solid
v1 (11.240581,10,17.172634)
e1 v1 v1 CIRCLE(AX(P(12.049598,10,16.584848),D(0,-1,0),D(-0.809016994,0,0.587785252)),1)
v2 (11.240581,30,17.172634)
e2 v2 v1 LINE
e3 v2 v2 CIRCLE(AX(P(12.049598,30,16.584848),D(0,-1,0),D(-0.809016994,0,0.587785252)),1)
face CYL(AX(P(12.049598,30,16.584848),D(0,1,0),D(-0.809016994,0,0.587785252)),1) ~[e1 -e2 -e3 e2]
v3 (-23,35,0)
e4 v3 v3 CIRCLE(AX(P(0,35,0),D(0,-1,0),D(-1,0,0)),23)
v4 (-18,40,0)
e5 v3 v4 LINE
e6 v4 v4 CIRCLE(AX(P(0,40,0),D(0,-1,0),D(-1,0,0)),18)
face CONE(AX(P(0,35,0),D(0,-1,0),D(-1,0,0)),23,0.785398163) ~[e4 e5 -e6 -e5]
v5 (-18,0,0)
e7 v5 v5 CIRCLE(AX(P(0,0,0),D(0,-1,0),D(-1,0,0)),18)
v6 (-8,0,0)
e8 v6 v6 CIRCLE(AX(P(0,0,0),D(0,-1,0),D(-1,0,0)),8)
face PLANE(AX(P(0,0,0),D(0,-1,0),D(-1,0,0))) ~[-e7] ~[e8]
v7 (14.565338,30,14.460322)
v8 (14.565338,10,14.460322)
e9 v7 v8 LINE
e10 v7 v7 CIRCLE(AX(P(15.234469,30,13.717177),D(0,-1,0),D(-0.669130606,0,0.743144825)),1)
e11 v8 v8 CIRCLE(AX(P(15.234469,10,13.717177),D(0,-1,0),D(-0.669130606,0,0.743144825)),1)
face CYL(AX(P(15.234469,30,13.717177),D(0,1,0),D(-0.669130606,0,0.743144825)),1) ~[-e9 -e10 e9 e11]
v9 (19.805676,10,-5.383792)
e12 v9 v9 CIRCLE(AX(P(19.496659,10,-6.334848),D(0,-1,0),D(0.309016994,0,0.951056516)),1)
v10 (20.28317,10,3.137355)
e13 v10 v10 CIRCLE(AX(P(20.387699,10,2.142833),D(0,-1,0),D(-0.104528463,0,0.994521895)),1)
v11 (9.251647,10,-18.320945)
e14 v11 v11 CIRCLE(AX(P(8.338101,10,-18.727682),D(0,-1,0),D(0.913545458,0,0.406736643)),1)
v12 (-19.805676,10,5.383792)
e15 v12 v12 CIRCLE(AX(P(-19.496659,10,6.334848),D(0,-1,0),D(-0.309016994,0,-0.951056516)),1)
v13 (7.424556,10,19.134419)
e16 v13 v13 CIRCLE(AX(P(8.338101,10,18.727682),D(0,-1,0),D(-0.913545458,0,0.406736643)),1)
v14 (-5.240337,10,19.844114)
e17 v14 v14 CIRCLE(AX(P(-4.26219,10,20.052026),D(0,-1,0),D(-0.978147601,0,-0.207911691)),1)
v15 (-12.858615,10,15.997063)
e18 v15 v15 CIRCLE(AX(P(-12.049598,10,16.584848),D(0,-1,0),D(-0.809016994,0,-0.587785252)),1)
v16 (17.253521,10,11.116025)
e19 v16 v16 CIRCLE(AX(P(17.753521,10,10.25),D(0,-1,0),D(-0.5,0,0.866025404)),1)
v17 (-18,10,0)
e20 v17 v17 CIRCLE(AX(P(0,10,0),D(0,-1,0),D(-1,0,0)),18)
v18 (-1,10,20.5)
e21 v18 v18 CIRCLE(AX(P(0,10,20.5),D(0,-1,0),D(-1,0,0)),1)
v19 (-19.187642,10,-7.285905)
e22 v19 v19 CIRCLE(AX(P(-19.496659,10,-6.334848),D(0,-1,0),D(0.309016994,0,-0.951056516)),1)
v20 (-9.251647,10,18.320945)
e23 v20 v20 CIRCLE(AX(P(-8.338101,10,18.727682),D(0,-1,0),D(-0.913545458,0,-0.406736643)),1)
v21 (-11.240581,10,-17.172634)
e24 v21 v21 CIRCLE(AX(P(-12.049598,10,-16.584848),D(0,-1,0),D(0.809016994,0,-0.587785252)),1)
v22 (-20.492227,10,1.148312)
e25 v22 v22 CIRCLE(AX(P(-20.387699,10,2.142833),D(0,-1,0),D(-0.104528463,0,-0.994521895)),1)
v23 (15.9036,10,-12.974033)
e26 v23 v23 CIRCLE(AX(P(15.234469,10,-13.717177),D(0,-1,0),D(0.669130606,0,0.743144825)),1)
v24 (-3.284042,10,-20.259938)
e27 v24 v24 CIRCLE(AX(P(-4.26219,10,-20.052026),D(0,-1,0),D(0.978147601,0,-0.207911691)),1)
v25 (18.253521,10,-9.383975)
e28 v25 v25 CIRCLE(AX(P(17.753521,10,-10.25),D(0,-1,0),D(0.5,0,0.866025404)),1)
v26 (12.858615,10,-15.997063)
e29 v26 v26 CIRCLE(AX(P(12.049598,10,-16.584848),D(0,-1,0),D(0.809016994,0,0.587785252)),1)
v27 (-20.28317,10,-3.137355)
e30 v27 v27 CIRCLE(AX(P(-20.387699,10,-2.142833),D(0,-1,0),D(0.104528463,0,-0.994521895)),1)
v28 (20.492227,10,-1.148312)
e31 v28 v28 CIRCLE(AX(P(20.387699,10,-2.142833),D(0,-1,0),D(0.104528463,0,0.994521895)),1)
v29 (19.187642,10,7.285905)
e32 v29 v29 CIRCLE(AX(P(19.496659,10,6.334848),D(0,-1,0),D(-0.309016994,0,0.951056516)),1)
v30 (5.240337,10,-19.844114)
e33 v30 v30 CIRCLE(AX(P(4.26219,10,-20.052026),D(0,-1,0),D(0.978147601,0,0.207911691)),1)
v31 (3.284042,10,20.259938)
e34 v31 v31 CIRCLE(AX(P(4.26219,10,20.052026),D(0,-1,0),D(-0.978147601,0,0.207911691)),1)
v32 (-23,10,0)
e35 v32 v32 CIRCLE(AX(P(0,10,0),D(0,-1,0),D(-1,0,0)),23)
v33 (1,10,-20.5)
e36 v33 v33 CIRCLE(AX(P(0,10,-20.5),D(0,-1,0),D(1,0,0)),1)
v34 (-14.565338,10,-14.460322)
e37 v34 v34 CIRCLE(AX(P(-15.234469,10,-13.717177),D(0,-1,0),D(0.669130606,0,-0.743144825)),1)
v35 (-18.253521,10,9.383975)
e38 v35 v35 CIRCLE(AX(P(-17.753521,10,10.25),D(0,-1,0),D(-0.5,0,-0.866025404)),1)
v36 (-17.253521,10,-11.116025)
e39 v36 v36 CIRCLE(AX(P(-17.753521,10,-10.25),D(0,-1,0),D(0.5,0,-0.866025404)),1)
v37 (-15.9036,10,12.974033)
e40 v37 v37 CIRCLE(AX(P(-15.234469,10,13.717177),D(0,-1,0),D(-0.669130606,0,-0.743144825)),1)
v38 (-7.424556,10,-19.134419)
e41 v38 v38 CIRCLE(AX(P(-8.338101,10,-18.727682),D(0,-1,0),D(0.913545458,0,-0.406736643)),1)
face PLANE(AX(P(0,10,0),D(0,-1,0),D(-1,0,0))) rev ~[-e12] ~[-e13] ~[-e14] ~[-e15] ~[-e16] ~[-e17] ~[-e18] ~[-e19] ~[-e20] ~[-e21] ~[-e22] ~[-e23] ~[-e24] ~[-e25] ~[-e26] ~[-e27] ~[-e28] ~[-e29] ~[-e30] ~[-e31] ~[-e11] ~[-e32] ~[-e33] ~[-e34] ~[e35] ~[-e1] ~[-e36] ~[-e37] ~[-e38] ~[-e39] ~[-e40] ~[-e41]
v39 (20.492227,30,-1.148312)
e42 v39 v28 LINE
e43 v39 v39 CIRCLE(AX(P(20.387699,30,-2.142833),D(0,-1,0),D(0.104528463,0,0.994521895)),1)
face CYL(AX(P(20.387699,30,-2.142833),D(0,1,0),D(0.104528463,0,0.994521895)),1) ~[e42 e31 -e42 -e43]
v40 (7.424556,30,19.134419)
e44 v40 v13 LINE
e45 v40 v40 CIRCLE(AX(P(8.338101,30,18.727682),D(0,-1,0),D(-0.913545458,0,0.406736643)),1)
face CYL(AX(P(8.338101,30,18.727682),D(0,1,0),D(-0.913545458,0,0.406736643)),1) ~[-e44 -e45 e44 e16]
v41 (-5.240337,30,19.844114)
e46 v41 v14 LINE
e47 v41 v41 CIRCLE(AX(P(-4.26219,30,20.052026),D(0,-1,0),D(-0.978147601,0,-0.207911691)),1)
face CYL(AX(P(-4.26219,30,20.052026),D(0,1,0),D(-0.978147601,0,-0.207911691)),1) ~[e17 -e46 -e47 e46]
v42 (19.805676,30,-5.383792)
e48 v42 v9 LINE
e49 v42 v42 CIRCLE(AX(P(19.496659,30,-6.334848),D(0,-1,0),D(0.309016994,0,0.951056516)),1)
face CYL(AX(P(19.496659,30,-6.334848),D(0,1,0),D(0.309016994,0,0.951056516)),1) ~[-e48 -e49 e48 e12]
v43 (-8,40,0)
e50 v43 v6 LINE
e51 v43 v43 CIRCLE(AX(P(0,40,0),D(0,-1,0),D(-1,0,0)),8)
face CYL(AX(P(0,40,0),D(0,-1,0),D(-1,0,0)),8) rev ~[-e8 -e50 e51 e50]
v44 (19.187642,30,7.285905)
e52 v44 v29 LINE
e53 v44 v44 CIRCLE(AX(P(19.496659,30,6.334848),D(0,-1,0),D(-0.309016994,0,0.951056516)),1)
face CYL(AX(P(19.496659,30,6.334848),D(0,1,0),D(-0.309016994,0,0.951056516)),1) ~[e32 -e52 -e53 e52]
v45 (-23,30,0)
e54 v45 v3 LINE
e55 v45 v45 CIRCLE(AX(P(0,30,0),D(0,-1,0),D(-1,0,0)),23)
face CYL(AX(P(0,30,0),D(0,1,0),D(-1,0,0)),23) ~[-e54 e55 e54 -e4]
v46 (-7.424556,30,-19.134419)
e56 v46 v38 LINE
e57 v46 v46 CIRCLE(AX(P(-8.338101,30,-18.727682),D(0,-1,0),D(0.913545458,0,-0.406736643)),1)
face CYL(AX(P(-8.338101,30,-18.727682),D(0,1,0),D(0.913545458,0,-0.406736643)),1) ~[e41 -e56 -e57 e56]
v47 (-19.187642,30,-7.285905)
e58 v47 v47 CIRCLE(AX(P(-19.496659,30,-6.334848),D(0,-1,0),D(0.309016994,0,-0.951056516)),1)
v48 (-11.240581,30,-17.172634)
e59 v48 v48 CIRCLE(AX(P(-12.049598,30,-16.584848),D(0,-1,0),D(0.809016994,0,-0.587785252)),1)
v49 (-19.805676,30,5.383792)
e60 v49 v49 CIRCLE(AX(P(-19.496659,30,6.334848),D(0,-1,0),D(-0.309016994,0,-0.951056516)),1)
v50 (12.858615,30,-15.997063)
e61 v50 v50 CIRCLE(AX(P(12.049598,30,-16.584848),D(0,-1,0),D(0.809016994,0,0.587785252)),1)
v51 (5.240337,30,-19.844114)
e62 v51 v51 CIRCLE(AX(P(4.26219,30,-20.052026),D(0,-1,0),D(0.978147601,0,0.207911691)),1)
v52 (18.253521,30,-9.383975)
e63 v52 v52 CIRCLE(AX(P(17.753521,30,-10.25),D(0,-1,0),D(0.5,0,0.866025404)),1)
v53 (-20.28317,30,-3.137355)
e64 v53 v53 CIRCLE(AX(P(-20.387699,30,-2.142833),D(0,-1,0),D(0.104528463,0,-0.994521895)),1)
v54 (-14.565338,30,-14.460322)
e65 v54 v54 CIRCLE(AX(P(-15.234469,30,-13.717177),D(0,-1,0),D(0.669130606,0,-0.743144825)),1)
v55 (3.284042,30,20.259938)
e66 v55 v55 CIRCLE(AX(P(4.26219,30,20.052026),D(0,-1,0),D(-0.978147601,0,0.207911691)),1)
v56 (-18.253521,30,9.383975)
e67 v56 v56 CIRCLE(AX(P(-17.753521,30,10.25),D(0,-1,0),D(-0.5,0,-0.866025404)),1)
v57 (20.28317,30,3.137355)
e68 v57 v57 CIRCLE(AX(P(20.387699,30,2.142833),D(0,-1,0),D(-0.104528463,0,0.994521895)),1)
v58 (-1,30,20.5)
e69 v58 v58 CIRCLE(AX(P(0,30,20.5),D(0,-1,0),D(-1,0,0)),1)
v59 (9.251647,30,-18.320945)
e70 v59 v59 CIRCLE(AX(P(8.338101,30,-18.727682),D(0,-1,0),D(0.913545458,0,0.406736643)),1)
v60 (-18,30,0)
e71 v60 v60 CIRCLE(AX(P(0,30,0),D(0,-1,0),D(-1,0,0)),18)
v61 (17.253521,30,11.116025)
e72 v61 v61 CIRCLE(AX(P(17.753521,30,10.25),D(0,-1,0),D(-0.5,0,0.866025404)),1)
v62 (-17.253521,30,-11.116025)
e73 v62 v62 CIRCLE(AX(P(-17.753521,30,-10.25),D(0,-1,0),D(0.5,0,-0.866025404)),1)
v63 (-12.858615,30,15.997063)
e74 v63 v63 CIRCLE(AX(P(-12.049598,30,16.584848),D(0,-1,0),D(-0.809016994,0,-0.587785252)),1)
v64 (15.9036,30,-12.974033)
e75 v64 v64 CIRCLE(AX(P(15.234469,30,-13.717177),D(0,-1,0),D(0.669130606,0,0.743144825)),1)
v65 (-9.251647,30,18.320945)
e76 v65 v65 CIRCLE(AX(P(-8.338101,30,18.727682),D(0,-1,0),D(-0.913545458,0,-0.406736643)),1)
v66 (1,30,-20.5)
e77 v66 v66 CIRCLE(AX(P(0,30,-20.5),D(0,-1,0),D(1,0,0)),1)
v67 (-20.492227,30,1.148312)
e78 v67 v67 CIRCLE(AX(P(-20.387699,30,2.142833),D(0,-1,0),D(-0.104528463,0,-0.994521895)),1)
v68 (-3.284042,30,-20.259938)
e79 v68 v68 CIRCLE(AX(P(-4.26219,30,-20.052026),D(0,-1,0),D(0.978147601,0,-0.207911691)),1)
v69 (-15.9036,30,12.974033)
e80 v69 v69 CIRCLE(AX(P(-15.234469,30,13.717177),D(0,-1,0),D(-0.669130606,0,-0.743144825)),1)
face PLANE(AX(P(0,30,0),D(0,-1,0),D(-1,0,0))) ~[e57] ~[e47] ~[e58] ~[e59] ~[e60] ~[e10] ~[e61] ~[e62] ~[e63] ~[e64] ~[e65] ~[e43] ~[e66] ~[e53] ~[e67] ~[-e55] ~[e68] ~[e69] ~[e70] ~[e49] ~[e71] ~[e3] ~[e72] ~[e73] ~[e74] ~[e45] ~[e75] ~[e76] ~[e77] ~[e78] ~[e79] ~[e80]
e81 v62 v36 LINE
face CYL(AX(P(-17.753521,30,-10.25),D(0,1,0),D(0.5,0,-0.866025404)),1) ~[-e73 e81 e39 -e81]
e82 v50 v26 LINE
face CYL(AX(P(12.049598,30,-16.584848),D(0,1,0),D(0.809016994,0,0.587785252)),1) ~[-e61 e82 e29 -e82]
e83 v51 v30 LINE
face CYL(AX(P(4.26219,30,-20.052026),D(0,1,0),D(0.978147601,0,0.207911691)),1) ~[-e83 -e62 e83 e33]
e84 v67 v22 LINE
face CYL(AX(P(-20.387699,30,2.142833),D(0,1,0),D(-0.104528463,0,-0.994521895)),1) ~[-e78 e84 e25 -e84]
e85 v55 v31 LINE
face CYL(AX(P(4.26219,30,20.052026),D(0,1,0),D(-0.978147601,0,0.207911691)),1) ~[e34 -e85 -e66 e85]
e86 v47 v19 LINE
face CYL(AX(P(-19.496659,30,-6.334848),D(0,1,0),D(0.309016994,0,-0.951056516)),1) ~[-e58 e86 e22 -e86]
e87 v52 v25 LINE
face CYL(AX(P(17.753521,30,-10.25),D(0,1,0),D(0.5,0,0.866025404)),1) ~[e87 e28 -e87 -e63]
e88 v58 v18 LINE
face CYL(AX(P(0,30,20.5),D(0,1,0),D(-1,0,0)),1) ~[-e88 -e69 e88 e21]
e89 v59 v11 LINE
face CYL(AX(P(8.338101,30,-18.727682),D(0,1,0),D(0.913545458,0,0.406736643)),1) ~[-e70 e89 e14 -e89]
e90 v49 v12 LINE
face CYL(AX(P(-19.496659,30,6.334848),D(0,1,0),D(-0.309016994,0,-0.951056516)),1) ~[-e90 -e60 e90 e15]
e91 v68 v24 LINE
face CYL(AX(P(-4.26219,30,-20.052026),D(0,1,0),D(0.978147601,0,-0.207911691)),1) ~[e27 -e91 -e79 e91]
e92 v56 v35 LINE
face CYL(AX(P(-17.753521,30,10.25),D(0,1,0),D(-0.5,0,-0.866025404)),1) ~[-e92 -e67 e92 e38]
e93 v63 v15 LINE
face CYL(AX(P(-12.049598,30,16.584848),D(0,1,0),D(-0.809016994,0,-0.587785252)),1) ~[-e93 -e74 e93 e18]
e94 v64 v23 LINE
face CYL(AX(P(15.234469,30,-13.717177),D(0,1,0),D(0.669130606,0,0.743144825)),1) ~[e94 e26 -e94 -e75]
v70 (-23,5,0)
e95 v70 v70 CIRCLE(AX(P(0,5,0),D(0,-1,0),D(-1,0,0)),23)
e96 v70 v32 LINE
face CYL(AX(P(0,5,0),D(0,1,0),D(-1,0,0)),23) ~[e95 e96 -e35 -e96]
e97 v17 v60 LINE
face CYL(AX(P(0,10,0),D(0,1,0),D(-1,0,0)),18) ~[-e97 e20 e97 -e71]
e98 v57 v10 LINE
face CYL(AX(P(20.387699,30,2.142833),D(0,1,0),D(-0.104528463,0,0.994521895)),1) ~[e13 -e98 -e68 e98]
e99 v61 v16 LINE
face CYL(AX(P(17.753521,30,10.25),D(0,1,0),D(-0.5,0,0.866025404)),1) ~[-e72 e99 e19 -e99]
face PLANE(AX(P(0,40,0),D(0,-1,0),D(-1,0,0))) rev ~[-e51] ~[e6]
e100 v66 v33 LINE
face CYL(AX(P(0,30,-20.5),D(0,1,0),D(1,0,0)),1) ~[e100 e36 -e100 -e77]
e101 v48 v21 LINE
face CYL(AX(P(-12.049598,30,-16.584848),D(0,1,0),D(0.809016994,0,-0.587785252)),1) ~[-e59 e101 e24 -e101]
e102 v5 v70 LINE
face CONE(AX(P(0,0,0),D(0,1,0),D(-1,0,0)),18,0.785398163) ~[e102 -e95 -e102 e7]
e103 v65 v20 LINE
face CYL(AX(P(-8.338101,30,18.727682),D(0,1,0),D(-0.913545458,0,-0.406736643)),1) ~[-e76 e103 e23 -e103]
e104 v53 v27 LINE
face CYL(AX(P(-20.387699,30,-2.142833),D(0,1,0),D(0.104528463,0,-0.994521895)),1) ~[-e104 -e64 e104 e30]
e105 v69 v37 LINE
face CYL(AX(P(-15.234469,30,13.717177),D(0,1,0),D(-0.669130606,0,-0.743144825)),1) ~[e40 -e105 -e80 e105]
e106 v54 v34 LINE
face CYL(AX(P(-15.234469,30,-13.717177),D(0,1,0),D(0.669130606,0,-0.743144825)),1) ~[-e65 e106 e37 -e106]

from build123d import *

# Parameters (mm, degrees)
TOOTH_PROFILE_R         = 1
TOOTH_DEPTH             = 20
TOOTH_PATTERN_30X_COUNT = 30


with BuildPart() as part:
    # Pulley Body Profile → Pulley Body (revolve)
    with BuildSketch(Plane.XY, mode=Mode.PRIVATE) as pulley_body_sk:
        Polygon((8, 40), (8, 0), (18, 0), (23, 5), (23, 10), (18, 10), (18, 30), (23, 30), (23, 35), (18, 40), align=None)
    revolve(pulley_body_sk.sketch.rotate(Axis((0, 32.636363636, 0), (0, -1, 0)), 180), axis=Axis((0, 32.636363636, 0), (0, -1, 0)))

    # Tooth Profile → Tooth (add)
    with BuildSketch(Plane.XZ.offset(-30)):
        with Locations(Location((0, 20.5, 0), (0, 0, 180))):
            Circle(TOOTH_PROFILE_R)
    tooth = extrude(amount=TOOTH_DEPTH)

    # Tooth Pattern 30x: Tooth ×30 about axis
    tooth_pattern_30x_axis = Axis((0, 0, 0), (0, 1, 0))
    for i in range(1, TOOTH_PATTERN_30X_COUNT):
        add(tooth.rotate(tooth_pattern_30x_axis, i * 360 / TOOTH_PATTERN_30X_COUNT))


solid = part.part
